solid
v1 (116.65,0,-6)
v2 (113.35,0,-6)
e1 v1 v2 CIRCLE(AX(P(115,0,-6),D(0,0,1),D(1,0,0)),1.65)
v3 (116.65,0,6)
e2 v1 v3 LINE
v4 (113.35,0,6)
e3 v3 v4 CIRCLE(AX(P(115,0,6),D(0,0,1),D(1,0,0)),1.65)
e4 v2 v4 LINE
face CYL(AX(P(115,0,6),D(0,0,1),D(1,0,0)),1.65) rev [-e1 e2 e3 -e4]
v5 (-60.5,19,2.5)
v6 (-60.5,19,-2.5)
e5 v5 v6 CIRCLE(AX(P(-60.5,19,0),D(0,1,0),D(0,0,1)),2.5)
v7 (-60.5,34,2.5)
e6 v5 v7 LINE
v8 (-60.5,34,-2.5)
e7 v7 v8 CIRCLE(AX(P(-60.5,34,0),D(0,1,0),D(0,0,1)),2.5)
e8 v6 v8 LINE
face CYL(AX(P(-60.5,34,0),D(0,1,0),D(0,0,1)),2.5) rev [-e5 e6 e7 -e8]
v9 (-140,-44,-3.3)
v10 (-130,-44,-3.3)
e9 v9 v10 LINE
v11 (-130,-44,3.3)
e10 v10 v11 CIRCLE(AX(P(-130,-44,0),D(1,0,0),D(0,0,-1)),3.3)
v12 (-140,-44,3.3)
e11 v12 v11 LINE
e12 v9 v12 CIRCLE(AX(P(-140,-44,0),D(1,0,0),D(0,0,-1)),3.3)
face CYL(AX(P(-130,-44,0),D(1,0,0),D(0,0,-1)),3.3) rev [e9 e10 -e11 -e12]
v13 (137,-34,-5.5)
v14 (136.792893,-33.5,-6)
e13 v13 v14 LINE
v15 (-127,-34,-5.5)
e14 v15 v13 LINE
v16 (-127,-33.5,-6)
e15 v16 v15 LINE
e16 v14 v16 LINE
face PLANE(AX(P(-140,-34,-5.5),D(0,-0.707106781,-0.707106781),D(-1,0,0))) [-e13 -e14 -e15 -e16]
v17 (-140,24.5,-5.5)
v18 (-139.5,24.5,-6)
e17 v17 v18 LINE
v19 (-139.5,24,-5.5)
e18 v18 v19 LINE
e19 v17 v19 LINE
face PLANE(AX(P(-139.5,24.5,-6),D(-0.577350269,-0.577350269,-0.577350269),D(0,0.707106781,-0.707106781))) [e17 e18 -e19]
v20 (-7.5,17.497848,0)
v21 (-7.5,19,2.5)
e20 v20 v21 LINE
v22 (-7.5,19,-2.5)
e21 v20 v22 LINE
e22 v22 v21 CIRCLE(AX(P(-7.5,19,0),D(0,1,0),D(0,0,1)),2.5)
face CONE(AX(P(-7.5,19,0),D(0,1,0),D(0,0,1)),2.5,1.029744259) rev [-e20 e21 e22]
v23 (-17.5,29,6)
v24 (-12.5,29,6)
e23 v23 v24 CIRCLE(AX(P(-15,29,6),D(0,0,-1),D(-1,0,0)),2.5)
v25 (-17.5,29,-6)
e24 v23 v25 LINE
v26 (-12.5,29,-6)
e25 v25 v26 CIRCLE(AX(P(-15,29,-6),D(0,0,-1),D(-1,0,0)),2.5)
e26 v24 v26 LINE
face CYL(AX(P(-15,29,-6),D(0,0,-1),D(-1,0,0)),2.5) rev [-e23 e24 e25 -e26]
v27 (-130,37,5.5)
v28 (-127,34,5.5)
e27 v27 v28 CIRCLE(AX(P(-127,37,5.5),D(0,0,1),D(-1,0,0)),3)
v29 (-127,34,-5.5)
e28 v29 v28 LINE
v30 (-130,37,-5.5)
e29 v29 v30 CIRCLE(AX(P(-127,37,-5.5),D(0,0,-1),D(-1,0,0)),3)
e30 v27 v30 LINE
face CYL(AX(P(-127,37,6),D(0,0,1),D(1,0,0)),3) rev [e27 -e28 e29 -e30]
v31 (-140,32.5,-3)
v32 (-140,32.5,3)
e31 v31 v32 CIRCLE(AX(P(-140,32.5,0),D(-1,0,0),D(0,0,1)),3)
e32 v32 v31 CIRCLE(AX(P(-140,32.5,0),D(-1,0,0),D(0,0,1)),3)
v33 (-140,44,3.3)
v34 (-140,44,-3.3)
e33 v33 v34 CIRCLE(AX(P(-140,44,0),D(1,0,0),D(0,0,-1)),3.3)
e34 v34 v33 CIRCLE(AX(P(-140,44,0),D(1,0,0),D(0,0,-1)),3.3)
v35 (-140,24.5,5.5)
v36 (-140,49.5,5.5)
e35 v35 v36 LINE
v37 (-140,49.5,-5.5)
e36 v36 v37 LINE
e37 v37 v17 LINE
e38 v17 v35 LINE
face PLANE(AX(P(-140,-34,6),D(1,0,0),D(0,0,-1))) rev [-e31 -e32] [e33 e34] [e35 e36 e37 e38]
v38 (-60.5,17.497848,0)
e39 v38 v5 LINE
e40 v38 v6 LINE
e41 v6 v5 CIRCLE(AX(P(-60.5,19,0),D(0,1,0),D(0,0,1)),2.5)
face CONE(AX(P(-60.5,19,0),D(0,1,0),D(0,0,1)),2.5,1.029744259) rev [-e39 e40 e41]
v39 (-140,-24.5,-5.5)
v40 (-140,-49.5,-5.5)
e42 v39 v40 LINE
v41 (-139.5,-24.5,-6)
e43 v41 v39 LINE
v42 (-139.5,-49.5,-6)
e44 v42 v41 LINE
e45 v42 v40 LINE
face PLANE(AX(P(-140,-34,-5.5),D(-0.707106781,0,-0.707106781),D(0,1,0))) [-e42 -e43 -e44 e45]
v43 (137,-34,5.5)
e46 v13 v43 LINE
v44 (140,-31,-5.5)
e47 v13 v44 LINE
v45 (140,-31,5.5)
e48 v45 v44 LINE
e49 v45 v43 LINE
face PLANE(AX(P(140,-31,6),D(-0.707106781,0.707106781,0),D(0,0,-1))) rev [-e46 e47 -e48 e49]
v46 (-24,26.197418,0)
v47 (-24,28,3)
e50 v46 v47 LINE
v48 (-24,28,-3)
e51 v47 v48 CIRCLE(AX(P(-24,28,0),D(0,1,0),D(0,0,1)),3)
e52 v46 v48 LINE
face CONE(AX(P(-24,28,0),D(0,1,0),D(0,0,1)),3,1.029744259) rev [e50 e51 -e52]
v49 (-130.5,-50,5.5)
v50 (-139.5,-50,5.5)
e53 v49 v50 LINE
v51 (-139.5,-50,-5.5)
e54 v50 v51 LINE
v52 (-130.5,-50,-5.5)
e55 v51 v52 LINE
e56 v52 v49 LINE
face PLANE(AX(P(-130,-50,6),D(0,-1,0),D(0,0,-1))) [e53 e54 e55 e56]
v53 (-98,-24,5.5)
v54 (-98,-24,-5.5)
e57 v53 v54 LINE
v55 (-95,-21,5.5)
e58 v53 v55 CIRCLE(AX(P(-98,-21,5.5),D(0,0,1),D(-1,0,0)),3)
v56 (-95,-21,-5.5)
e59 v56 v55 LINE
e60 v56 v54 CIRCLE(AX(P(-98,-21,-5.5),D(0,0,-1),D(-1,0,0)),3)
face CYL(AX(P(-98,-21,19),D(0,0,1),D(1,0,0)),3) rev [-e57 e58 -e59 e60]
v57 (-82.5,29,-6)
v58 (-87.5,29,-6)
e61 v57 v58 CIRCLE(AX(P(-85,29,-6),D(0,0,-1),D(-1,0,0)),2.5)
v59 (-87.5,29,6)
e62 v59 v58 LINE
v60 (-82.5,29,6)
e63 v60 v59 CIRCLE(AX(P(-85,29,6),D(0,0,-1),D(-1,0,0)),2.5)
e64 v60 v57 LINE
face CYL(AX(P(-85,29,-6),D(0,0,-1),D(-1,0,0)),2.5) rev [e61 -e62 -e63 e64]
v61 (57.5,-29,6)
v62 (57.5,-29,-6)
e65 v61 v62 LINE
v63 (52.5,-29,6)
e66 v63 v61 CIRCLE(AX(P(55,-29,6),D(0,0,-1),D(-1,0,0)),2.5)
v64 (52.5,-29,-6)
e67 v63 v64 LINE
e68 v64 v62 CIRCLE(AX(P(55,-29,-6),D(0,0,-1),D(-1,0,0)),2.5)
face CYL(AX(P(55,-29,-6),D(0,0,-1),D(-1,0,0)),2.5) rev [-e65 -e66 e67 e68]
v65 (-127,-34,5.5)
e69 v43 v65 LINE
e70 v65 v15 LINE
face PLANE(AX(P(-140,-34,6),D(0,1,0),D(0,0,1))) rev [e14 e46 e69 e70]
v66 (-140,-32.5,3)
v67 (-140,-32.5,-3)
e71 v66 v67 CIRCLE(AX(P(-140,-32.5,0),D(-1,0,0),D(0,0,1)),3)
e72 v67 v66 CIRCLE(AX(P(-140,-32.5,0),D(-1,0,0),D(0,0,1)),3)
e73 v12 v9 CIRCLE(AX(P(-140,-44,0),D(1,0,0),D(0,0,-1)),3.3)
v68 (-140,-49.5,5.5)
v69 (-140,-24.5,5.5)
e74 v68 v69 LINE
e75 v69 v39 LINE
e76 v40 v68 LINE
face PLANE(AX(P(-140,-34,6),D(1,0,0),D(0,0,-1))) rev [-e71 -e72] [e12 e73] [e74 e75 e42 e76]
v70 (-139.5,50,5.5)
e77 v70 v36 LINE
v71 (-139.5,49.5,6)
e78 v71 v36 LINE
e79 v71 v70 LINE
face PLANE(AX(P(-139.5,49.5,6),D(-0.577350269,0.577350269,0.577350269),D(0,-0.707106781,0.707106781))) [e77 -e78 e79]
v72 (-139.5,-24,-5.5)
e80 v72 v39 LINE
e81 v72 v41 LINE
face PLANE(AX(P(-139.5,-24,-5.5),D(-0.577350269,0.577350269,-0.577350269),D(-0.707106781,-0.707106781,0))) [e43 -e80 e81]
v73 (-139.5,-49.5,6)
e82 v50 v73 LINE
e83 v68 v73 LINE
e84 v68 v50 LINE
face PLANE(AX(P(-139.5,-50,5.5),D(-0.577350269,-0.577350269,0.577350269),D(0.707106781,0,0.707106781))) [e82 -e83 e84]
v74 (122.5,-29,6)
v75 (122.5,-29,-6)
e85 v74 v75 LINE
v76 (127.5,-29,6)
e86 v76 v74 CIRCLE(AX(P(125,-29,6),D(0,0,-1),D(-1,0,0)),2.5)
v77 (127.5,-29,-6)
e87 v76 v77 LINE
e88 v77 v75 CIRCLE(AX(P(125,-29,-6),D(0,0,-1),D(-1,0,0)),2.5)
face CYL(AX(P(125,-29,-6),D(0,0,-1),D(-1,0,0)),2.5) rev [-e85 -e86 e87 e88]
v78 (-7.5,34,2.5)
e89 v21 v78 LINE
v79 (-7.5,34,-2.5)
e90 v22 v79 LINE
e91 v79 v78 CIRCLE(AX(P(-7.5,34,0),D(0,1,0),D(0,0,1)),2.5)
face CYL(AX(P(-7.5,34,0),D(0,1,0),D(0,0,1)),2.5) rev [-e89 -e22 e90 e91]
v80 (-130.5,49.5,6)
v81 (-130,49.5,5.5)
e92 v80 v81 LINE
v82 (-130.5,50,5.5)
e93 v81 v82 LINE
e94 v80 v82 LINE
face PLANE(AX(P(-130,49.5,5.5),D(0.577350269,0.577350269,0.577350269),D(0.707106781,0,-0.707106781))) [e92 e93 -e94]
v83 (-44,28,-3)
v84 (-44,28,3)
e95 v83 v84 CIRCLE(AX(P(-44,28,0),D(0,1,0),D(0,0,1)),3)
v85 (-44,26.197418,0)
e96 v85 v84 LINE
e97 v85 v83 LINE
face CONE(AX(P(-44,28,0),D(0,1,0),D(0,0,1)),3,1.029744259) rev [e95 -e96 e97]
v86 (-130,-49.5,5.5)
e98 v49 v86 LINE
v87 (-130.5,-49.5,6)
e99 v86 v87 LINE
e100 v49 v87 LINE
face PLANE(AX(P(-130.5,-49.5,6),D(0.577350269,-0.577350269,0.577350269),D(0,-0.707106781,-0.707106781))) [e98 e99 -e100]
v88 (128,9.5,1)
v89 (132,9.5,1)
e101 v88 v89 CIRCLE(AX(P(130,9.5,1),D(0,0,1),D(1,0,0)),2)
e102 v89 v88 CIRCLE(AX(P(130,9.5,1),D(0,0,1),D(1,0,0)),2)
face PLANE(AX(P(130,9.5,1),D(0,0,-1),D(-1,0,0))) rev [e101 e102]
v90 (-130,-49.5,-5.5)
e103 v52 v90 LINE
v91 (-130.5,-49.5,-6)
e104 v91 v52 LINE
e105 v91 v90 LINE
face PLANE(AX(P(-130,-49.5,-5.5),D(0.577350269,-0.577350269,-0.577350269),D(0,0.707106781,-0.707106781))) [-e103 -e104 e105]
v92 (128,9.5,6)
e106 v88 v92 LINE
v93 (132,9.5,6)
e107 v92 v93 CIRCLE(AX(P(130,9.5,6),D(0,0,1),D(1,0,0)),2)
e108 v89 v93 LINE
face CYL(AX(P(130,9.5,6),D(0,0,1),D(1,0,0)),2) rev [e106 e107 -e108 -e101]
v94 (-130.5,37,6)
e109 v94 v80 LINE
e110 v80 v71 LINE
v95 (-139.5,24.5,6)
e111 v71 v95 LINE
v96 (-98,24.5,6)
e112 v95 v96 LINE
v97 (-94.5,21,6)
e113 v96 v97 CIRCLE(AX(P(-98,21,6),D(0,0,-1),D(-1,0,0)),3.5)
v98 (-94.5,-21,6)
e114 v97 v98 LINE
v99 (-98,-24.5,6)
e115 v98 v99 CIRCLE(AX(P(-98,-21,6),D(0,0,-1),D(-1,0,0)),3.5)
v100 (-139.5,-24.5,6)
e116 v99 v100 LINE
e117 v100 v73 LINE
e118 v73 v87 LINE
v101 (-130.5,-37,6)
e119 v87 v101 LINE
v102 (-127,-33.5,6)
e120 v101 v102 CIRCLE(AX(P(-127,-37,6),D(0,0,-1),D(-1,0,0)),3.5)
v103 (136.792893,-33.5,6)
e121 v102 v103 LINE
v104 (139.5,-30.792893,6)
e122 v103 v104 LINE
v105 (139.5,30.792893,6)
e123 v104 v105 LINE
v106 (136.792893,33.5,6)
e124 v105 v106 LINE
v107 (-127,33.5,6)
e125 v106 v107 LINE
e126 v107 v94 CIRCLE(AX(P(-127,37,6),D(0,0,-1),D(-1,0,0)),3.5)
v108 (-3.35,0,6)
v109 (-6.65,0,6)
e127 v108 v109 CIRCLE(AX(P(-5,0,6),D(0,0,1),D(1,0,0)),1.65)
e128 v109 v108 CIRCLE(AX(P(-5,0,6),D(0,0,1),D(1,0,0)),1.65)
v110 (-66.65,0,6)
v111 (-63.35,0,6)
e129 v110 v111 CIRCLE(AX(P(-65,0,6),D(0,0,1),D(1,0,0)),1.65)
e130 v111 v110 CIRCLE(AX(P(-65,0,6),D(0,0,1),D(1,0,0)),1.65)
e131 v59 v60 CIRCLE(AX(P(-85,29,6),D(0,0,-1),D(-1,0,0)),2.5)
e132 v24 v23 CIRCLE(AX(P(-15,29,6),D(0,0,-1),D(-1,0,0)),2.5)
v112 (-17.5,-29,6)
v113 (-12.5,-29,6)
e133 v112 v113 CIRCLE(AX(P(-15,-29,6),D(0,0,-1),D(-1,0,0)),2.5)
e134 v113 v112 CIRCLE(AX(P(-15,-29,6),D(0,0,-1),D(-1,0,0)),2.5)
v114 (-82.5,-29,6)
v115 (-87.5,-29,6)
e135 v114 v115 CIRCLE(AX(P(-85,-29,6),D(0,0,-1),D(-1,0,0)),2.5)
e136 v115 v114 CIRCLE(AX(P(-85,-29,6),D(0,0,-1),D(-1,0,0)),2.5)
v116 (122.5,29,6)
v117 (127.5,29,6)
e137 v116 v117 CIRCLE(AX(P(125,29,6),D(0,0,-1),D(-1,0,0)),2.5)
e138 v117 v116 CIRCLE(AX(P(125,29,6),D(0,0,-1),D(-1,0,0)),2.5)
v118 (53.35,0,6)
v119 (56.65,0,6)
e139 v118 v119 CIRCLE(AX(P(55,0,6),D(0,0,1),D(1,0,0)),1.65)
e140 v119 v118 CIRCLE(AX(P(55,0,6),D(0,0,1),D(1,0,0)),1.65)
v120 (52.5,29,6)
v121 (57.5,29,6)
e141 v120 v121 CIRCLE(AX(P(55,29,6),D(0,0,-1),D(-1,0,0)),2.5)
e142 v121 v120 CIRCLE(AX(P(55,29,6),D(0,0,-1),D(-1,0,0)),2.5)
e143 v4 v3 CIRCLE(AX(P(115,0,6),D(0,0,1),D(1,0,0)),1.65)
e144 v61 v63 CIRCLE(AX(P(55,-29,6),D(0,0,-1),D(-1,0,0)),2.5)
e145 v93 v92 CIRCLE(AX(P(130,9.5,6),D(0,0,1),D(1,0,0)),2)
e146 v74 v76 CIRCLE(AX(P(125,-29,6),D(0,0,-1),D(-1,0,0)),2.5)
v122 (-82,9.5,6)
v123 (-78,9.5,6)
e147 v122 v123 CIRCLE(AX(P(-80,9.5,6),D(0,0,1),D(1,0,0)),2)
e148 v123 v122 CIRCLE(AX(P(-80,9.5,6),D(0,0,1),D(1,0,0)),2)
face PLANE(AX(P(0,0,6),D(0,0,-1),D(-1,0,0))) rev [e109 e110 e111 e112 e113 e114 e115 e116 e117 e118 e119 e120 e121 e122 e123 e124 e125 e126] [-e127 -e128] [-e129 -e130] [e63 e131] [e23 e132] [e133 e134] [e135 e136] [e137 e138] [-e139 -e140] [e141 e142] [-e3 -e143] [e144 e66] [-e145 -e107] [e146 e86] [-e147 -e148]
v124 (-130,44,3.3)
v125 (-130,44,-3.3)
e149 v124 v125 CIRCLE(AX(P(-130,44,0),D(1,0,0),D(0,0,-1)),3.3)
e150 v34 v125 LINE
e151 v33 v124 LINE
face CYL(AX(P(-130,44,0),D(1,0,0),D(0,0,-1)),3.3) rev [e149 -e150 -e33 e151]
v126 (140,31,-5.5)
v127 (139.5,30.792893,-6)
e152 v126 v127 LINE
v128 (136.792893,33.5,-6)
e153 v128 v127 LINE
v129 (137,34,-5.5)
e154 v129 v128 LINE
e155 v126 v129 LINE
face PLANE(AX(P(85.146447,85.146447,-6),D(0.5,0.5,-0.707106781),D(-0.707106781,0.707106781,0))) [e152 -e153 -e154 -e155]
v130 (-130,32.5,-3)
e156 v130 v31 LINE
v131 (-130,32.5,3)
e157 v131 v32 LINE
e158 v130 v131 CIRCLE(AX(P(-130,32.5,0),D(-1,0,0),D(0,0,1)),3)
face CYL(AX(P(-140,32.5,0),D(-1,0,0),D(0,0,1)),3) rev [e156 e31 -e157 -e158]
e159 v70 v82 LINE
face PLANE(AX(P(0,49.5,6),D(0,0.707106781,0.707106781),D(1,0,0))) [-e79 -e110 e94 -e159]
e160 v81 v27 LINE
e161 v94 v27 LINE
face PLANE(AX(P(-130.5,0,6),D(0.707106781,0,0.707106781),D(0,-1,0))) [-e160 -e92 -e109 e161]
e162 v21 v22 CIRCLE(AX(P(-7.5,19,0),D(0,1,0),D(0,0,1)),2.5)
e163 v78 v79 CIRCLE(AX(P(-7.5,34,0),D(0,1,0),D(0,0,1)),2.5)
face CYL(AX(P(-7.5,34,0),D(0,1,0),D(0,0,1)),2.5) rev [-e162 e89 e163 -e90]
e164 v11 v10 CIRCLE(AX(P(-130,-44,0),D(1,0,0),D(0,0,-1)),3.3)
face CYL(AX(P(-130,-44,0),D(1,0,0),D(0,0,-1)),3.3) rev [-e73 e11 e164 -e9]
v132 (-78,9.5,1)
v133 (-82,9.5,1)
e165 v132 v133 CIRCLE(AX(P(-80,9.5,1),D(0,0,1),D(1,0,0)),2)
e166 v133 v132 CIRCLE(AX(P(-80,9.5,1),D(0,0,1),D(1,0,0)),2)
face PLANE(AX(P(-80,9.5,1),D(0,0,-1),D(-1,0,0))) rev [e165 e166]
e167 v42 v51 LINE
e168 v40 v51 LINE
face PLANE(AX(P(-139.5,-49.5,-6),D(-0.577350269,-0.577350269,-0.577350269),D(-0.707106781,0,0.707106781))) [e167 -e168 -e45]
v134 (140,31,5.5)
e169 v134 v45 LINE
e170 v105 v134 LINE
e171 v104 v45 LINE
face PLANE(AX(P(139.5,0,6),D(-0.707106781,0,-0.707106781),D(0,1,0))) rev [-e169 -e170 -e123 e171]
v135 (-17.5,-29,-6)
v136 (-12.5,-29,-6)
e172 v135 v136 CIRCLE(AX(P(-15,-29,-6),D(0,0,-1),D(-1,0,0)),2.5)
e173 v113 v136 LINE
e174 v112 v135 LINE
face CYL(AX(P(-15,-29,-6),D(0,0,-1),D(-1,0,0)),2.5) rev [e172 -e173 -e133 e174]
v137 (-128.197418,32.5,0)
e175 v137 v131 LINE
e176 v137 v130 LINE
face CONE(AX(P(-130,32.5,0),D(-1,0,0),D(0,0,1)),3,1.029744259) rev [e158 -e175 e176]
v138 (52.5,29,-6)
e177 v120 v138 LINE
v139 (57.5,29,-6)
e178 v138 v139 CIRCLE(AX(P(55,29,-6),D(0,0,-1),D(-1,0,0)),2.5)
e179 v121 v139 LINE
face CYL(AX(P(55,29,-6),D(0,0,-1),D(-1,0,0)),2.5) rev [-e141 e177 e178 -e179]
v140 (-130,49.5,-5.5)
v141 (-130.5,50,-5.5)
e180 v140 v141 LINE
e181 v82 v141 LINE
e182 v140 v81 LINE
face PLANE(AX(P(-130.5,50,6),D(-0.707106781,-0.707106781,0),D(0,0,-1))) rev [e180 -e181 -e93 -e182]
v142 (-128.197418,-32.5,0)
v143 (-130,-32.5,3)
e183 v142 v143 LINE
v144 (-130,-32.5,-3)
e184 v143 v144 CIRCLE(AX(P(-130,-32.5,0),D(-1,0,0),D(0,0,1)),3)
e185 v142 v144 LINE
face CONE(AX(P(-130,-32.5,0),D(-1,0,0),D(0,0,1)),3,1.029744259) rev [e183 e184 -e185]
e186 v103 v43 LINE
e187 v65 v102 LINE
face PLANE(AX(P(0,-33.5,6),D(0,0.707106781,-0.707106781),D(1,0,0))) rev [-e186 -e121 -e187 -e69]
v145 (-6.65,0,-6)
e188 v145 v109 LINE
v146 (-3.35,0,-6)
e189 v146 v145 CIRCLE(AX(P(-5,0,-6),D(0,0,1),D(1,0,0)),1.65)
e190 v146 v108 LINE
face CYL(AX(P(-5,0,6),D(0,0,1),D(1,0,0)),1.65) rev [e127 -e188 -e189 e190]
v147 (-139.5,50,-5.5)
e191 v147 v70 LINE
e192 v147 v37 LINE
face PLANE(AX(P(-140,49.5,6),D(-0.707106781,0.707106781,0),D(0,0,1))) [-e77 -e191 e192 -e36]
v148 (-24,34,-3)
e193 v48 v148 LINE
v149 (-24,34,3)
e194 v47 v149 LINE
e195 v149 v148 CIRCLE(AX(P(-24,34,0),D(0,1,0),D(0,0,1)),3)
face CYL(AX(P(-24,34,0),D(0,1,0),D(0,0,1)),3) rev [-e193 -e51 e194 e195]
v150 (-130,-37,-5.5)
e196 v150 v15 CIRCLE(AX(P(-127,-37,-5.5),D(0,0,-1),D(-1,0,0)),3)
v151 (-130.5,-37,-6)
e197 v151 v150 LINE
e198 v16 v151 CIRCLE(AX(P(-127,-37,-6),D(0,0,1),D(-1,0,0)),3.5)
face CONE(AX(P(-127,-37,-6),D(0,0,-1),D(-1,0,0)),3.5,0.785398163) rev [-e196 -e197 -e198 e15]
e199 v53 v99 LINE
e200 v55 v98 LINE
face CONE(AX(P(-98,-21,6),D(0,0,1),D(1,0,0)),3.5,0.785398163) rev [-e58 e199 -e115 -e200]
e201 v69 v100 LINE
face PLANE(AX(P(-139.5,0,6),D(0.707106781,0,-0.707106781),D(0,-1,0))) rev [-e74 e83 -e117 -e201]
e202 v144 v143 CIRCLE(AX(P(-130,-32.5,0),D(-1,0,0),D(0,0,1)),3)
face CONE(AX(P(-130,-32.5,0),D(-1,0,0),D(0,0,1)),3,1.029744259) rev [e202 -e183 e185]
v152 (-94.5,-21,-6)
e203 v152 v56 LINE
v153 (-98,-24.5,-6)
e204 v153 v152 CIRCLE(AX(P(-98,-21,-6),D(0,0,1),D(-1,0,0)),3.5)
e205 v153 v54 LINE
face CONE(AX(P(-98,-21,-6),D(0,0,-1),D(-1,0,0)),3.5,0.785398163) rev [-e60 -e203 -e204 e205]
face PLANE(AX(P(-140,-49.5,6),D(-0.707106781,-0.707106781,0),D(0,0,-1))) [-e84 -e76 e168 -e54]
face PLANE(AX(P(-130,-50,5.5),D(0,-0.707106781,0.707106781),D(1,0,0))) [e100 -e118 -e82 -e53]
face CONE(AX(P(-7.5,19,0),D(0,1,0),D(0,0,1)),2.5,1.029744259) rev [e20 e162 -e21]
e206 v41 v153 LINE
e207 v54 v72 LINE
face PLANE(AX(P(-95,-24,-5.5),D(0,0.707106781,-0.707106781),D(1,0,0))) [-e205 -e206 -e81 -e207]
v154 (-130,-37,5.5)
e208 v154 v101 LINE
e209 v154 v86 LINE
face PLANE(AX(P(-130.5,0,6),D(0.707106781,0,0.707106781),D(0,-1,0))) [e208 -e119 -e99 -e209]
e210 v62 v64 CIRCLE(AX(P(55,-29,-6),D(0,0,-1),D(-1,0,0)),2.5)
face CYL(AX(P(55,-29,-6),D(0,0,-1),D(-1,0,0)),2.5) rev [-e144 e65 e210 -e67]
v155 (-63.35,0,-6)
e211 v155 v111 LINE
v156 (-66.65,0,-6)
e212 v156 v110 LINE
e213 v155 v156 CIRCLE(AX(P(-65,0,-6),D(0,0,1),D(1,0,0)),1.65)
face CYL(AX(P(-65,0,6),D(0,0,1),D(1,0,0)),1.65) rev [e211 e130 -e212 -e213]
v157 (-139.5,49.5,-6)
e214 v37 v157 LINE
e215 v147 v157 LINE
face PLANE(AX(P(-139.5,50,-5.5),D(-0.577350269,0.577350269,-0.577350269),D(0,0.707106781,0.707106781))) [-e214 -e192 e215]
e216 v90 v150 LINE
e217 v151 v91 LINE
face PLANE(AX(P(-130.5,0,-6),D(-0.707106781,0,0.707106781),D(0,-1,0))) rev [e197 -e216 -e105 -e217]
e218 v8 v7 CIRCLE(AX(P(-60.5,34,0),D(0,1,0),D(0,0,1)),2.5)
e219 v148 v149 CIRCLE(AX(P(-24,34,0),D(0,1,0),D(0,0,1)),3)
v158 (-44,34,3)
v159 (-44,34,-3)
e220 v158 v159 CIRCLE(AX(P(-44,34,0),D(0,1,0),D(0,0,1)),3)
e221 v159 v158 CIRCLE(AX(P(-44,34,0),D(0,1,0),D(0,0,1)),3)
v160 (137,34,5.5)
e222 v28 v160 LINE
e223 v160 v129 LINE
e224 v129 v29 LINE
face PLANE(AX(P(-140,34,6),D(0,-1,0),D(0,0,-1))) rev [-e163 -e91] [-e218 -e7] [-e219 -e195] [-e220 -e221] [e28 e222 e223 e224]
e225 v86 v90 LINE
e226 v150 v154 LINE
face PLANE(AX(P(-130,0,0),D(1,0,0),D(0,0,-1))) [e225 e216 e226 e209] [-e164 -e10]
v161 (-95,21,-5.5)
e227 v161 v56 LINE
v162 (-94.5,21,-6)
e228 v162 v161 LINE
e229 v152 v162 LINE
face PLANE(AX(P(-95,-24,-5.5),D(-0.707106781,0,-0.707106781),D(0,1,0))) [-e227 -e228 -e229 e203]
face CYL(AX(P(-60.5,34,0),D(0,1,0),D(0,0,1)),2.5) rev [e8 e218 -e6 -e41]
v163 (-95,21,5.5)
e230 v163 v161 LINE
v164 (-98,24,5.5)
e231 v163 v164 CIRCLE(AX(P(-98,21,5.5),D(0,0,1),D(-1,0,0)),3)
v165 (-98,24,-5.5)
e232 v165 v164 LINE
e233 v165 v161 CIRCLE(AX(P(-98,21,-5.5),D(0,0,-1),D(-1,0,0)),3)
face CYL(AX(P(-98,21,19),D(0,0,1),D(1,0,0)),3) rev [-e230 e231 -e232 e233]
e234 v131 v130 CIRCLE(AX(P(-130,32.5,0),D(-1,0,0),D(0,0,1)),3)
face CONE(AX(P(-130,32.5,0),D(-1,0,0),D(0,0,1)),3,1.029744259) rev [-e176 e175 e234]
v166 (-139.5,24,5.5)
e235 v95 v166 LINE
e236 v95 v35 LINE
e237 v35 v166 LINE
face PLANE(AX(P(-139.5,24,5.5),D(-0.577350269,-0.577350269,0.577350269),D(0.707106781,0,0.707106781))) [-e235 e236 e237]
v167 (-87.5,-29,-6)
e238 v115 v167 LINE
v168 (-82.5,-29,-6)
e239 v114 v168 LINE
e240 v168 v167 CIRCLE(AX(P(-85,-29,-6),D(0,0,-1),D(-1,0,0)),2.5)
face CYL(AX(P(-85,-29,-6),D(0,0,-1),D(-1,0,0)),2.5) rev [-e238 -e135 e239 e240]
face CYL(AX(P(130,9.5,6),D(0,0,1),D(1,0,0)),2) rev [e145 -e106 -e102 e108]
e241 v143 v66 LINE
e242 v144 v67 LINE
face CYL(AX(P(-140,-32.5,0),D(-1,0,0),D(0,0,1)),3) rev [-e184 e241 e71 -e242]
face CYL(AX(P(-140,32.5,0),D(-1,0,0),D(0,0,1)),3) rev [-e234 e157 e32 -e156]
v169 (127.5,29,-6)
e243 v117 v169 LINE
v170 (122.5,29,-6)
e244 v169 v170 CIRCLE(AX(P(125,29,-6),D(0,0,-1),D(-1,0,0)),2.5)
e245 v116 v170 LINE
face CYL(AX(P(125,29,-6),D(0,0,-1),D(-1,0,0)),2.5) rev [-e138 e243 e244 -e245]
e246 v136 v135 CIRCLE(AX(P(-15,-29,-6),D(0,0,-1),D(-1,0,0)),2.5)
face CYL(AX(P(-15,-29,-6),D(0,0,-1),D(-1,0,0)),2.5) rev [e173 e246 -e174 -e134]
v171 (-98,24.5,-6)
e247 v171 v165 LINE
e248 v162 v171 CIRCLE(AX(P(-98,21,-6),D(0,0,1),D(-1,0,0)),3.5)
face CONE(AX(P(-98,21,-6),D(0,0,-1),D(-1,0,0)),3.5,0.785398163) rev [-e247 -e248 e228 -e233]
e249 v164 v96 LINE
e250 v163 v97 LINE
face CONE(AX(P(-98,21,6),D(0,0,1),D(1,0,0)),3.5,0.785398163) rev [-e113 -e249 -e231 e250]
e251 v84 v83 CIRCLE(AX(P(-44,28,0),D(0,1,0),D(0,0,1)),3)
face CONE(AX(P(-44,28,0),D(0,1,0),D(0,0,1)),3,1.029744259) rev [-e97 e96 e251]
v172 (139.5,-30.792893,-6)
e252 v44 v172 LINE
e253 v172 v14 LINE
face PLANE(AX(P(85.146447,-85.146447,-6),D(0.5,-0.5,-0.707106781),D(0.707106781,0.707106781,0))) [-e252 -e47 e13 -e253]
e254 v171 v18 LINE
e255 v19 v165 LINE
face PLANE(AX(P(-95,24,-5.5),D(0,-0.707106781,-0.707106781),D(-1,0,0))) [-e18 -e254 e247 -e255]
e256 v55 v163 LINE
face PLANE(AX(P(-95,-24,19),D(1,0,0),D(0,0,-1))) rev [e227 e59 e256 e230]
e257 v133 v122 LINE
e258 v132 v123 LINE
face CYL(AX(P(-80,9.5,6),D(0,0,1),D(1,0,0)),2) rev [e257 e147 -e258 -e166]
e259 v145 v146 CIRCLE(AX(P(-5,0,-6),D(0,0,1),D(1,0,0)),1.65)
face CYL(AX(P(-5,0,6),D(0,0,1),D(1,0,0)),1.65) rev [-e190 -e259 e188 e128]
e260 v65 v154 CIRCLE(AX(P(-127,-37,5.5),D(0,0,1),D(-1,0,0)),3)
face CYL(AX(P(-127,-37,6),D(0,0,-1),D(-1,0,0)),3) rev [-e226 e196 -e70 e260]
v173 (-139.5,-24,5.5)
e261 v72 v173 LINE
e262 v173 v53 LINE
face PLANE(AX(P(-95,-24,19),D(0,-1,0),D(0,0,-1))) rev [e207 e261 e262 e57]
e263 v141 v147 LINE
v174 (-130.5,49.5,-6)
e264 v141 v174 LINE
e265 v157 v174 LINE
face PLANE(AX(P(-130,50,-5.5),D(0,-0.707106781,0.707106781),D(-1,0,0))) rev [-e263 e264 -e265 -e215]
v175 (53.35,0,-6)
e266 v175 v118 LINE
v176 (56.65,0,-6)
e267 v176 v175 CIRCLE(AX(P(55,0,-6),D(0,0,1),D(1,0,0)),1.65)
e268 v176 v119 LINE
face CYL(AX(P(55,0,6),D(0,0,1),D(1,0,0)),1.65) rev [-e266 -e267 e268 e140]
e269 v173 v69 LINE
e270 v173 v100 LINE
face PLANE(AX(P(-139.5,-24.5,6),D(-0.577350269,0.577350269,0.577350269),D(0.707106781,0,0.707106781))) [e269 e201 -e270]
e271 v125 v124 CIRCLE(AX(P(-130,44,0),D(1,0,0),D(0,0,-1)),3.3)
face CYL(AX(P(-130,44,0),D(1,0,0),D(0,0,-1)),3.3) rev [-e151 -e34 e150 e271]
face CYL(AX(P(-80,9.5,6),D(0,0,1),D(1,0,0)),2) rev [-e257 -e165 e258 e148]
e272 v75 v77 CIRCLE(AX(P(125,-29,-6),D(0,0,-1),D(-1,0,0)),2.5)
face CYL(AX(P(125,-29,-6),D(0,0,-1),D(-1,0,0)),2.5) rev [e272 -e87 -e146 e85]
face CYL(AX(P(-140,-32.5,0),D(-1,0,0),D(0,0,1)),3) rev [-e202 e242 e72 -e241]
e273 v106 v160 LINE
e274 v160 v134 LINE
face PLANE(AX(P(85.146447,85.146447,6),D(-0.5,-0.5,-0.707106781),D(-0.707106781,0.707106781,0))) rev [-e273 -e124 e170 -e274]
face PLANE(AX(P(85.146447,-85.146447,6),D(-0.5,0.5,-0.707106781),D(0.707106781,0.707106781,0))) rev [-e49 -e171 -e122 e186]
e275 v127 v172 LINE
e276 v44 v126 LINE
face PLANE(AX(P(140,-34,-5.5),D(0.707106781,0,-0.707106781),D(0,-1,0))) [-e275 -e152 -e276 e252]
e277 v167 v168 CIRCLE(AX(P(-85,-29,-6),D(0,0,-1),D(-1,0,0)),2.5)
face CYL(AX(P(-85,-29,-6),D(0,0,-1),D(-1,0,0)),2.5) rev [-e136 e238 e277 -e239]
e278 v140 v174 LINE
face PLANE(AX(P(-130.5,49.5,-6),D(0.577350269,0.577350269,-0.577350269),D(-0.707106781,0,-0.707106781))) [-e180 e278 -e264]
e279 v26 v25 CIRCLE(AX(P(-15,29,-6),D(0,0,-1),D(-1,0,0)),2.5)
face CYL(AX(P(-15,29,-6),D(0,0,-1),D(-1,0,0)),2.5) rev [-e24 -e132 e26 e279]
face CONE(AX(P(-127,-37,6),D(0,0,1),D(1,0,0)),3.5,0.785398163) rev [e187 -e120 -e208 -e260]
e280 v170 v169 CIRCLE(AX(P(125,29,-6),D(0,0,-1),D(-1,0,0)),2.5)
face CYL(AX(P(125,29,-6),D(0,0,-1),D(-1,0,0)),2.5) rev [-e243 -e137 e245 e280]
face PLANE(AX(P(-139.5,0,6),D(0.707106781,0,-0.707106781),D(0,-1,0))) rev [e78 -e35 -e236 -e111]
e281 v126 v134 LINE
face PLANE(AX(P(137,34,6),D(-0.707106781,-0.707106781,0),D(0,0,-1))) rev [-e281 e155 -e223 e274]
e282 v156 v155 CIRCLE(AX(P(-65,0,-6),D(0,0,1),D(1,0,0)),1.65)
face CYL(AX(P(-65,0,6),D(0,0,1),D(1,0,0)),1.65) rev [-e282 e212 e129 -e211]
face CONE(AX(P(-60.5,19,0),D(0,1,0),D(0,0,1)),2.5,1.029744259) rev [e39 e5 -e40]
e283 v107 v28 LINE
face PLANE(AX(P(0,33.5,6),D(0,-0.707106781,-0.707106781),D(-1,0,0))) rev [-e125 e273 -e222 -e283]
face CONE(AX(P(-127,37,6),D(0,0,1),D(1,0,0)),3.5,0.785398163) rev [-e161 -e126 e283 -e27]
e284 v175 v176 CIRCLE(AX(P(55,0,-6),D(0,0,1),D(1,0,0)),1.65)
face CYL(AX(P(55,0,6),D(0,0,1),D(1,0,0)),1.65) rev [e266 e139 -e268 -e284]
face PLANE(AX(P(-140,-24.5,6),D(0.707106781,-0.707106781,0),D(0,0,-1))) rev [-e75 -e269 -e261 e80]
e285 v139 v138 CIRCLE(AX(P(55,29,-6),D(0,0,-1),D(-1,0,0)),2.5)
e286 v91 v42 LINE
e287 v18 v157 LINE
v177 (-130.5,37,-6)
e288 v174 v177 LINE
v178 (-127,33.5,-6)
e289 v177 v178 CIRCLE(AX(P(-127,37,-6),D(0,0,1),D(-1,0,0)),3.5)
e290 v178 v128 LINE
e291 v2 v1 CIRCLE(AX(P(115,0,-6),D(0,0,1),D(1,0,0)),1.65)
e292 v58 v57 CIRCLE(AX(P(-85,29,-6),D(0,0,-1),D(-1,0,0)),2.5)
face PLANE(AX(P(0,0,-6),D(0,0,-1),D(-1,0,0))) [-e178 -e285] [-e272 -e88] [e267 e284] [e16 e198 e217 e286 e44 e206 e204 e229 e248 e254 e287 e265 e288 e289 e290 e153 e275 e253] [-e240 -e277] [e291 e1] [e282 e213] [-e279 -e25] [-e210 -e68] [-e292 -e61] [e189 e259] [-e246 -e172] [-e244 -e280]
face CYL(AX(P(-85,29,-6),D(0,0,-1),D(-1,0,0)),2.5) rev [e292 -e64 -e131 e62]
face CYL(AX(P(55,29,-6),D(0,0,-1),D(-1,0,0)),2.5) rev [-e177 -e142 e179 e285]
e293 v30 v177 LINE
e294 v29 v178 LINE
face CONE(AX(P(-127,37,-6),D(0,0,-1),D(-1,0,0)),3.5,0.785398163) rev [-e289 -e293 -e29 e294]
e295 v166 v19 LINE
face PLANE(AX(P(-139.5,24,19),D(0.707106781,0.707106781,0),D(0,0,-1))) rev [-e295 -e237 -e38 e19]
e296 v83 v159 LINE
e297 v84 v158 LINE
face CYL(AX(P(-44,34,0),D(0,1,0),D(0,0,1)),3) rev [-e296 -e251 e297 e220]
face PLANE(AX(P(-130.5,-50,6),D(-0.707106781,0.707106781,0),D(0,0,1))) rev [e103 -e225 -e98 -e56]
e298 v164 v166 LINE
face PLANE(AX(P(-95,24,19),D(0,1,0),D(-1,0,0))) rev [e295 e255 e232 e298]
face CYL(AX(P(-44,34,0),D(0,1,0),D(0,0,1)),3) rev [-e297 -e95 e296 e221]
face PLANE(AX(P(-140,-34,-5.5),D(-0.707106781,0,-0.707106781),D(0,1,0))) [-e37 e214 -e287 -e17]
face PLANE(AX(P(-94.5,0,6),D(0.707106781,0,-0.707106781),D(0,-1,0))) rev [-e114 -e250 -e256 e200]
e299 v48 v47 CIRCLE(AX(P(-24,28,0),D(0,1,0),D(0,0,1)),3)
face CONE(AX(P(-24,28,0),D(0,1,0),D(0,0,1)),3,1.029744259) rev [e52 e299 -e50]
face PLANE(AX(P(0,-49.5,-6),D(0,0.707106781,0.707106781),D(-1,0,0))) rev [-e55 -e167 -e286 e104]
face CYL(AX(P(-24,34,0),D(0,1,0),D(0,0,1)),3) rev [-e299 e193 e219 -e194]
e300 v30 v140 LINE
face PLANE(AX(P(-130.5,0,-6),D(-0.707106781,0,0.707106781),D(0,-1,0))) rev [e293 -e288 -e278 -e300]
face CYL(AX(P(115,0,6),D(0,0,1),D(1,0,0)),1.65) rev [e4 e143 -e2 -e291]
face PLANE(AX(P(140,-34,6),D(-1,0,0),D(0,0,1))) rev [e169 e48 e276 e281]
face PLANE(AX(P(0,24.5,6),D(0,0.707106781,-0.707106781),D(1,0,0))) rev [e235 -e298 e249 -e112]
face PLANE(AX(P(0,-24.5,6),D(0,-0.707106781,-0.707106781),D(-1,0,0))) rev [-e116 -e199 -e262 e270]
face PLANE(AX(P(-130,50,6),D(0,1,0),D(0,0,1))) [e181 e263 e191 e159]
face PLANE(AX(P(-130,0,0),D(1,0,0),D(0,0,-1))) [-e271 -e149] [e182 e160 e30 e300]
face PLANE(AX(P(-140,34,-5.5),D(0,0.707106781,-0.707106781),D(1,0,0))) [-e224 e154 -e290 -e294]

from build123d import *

# Parameters (mm, degrees)
SKETCH_1_W             = 280
SKETCH_1_H             = 68
EXTRUDE_1_DEPTH        = 6
SKETCH_2_W             = 45
SKETCH_2_H             = 48
CUT_EXTRUDE_1_DEPTH    = 25
FILLET_1_R             = 3
SKETCH_3_W             = 12
SKETCH_3_H             = 16
EXTRUDE_2_DEPTH        = 10
FILLET_2_R             = 3
HOLE_WIZARD_M6_1_D     = 6.6
F_6_0MM_1_D            = 6
F_6_0MM_1_DEPTH        = 10
F_6_0MM_1_TIP          = 1.802581857
CHAMFER_1_SIZE         = 3
CHAMFER_2_SIZE         = 0.5
HOLE_WIZARD_M6_3_D     = 5
F_6_0MM_2_D            = 6
F_6_0MM_2_DEPTH        = 6
F_6_0MM_2_TIP          = 1.802581857
HOLE_WIZARD_M6_4_D     = 5
HOLE_WIZARD_M6_4_DEPTH = 15
HOLE_WIZARD_M6_4_TIP   = 1.502151548
HOLE_WIZARD_M4_1_D     = 3.3
F_4_0_MM_1_D           = 4
F_4_0_MM_1_DEPTH       = 5


with BuildPart() as part:
    # 草图1 → 凸台-拉伸1 (new, symmetric)
    with BuildSketch(Plane.XY):
        Rectangle(SKETCH_1_W, SKETCH_1_H)
    extrude(amount=EXTRUDE_1_DEPTH, both=True)

    # 草图2 → 切除-拉伸1 (cut)
    with BuildSketch(Plane(origin=(0, 0, -6), x_dir=(-1, 0, 0), z_dir=(0, 0, -1))):
        with Locations((117.5, 0)):
            Rectangle(SKETCH_2_W, SKETCH_2_H)
    extrude(amount=-CUT_EXTRUDE_1_DEPTH, mode=Mode.SUBTRACT)

    # 圆角1
    fillet_1_edges = [part.edges().sort_by_distance(p)[0] for p in [
        (-95, -24, 0),
        (-95, 24, 0),
    ]]
    fillet(fillet_1_edges, radius=FILLET_1_R)

    # 草图3 → 凸台-拉伸2 (add)
    with BuildSketch(Plane.ZY.offset(140)):
        with Locations((0, -42)):
            Rectangle(SKETCH_3_W, SKETCH_3_H)
        with Locations((0, 42)):
            Rectangle(SKETCH_3_W, SKETCH_3_H)
    extrude(amount=-EXTRUDE_2_DEPTH)

    # 圆角2
    fillet_2_edges = [part.edges().sort_by_distance(p)[0] for p in [
        (-130, -34, 0),
        (-130, 34, 0),
    ]]
    fillet(fillet_2_edges, radius=FILLET_2_R)

    # M6 间隙孔1 (through all)
    with Locations(Plane(origin=(-130, 0, 0), x_dir=(0, 0, -1), z_dir=(1, 0, 0))):
        with Locations((0, -44), (0, 44)):
            Hole(HOLE_WIZARD_M6_1_D / 2)

    # Ø6.0mm 暗销孔1
    with Locations(Plane.ZY.offset(140)):
        with Locations((0, 32.5), (0, -32.5)):
            Hole(F_6_0MM_1_D / 2, depth=F_6_0MM_1_DEPTH)
            with Locations((0, 0, -(F_6_0MM_1_DEPTH + F_6_0MM_1_TIP / 2))):  # 118° drill point
                Cone(0, F_6_0MM_1_D / 2, F_6_0MM_1_TIP, mode=Mode.SUBTRACT)

    # 倒角1
    chamfer_1_edges = [part.edges().sort_by_distance(p)[0] for p in [
        (140, -34, 0),
        (140, 34, 0),
    ]]
    chamfer(chamfer_1_edges, length=CHAMFER_1_SIZE)

    # 倒角2
    chamfer_2_edges = [part.edges().sort_by_distance(p)[0] for p in [
        (-140, 37, 6),
        (5, 34, -6),
        (5, 34, 6),
        (140, 0, -6),
        (138.5, -32.5, -6),
        (138.5, 32.5, -6),
        (140, 0, 6),
        (138.5, -32.5, 6),
        (138.5, 32.5, 6),
        (-140, -37, -6),
        (-140, -37, 6),
        (-119, 24, 6),
        (-140, 24, 0),
        (-140, -24, 0),
        (-119, 24, -6),
        (-119, -24, -6),
        (-119, -24, 6),
        (-95, 0, -6),
        (-95, 0, 6),
        (-95.878679656, -23.121320344, -6),
        (-95.878679656, -23.121320344, 6),
        (-95.878679656, 23.121320344, -6),
        (-95.878679656, 23.121320344, 6),
        (-130, -43.5, 6),
        (-140, 37, -6),
        (-130, -50, 0),
        (-135, -50, 6),
        (-135, -50, -6),
        (-140, -50, 0),
        (-130, 43.5, -6),
        (-130, 50, 0),
        (-135, 50, -6),
        (-135, 50, 6),
        (-140, 50, 0),
        (-130, 43.5, 6),
        (5, -34, 6),
        (5, -34, -6),
        (-130, -43.5, -6),
        (-129.121320344, 34.878679656, 6),
        (-129.121320344, 34.878679656, -6),
        (-129.121320344, -34.878679656, -6),
        (-129.121320344, -34.878679656, 6),
    ]]
    chamfer(chamfer_2_edges, length=CHAMFER_2_SIZE)

    # M6 螺纹孔3 (through all)
    with Locations(Plane(origin=(0, 0, -6), x_dir=(-1, 0, 0), z_dir=(0, 0, -1))):
        with Locations((-125, 29), (-125, -29), (-55, 29), (-55, -29), (15, 29), (15, -29), (85, 29), (85, -29)):
            Hole(HOLE_WIZARD_M6_3_D / 2)

    # Ø6.0mm 暗销孔2
    with Locations(Plane(origin=(0, 34, 0), x_dir=(1, 0, 0), z_dir=(0, 1, 0))):
        with Locations((-24, 0), (-44, 0)):
            Hole(F_6_0MM_2_D / 2, depth=F_6_0MM_2_DEPTH)
            with Locations((0, 0, -(F_6_0MM_2_DEPTH + F_6_0MM_2_TIP / 2))):  # 118° drill point
                Cone(0, F_6_0MM_2_D / 2, F_6_0MM_2_TIP, mode=Mode.SUBTRACT)

    # M6 螺纹孔4
    with Locations(Plane(origin=(0, 34, 0), x_dir=(1, 0, 0), z_dir=(0, 1, 0))):
        with Locations((-7.5, 0), (-60.5, 0)):
            Hole(HOLE_WIZARD_M6_4_D / 2, depth=HOLE_WIZARD_M6_4_DEPTH)
            with Locations((0, 0, -(HOLE_WIZARD_M6_4_DEPTH + HOLE_WIZARD_M6_4_TIP / 2))):  # 118° drill point
                Cone(0, HOLE_WIZARD_M6_4_D / 2, HOLE_WIZARD_M6_4_TIP, mode=Mode.SUBTRACT)

    # M4 螺纹孔1 (through all)
    with Locations(Plane.XY.offset(6)):
        with Locations((115, 0), (55, 0), (-65, 0), (-5, 0)):
            Hole(HOLE_WIZARD_M4_1_D / 2)

    # Ø4.0 mm 暗销孔1
    with Locations(Plane.XY.offset(6)):
        with Locations((-80, 9.5), (130, 9.5)):
            Hole(F_4_0_MM_1_D / 2, depth=F_4_0_MM_1_DEPTH)


solid = part.part
